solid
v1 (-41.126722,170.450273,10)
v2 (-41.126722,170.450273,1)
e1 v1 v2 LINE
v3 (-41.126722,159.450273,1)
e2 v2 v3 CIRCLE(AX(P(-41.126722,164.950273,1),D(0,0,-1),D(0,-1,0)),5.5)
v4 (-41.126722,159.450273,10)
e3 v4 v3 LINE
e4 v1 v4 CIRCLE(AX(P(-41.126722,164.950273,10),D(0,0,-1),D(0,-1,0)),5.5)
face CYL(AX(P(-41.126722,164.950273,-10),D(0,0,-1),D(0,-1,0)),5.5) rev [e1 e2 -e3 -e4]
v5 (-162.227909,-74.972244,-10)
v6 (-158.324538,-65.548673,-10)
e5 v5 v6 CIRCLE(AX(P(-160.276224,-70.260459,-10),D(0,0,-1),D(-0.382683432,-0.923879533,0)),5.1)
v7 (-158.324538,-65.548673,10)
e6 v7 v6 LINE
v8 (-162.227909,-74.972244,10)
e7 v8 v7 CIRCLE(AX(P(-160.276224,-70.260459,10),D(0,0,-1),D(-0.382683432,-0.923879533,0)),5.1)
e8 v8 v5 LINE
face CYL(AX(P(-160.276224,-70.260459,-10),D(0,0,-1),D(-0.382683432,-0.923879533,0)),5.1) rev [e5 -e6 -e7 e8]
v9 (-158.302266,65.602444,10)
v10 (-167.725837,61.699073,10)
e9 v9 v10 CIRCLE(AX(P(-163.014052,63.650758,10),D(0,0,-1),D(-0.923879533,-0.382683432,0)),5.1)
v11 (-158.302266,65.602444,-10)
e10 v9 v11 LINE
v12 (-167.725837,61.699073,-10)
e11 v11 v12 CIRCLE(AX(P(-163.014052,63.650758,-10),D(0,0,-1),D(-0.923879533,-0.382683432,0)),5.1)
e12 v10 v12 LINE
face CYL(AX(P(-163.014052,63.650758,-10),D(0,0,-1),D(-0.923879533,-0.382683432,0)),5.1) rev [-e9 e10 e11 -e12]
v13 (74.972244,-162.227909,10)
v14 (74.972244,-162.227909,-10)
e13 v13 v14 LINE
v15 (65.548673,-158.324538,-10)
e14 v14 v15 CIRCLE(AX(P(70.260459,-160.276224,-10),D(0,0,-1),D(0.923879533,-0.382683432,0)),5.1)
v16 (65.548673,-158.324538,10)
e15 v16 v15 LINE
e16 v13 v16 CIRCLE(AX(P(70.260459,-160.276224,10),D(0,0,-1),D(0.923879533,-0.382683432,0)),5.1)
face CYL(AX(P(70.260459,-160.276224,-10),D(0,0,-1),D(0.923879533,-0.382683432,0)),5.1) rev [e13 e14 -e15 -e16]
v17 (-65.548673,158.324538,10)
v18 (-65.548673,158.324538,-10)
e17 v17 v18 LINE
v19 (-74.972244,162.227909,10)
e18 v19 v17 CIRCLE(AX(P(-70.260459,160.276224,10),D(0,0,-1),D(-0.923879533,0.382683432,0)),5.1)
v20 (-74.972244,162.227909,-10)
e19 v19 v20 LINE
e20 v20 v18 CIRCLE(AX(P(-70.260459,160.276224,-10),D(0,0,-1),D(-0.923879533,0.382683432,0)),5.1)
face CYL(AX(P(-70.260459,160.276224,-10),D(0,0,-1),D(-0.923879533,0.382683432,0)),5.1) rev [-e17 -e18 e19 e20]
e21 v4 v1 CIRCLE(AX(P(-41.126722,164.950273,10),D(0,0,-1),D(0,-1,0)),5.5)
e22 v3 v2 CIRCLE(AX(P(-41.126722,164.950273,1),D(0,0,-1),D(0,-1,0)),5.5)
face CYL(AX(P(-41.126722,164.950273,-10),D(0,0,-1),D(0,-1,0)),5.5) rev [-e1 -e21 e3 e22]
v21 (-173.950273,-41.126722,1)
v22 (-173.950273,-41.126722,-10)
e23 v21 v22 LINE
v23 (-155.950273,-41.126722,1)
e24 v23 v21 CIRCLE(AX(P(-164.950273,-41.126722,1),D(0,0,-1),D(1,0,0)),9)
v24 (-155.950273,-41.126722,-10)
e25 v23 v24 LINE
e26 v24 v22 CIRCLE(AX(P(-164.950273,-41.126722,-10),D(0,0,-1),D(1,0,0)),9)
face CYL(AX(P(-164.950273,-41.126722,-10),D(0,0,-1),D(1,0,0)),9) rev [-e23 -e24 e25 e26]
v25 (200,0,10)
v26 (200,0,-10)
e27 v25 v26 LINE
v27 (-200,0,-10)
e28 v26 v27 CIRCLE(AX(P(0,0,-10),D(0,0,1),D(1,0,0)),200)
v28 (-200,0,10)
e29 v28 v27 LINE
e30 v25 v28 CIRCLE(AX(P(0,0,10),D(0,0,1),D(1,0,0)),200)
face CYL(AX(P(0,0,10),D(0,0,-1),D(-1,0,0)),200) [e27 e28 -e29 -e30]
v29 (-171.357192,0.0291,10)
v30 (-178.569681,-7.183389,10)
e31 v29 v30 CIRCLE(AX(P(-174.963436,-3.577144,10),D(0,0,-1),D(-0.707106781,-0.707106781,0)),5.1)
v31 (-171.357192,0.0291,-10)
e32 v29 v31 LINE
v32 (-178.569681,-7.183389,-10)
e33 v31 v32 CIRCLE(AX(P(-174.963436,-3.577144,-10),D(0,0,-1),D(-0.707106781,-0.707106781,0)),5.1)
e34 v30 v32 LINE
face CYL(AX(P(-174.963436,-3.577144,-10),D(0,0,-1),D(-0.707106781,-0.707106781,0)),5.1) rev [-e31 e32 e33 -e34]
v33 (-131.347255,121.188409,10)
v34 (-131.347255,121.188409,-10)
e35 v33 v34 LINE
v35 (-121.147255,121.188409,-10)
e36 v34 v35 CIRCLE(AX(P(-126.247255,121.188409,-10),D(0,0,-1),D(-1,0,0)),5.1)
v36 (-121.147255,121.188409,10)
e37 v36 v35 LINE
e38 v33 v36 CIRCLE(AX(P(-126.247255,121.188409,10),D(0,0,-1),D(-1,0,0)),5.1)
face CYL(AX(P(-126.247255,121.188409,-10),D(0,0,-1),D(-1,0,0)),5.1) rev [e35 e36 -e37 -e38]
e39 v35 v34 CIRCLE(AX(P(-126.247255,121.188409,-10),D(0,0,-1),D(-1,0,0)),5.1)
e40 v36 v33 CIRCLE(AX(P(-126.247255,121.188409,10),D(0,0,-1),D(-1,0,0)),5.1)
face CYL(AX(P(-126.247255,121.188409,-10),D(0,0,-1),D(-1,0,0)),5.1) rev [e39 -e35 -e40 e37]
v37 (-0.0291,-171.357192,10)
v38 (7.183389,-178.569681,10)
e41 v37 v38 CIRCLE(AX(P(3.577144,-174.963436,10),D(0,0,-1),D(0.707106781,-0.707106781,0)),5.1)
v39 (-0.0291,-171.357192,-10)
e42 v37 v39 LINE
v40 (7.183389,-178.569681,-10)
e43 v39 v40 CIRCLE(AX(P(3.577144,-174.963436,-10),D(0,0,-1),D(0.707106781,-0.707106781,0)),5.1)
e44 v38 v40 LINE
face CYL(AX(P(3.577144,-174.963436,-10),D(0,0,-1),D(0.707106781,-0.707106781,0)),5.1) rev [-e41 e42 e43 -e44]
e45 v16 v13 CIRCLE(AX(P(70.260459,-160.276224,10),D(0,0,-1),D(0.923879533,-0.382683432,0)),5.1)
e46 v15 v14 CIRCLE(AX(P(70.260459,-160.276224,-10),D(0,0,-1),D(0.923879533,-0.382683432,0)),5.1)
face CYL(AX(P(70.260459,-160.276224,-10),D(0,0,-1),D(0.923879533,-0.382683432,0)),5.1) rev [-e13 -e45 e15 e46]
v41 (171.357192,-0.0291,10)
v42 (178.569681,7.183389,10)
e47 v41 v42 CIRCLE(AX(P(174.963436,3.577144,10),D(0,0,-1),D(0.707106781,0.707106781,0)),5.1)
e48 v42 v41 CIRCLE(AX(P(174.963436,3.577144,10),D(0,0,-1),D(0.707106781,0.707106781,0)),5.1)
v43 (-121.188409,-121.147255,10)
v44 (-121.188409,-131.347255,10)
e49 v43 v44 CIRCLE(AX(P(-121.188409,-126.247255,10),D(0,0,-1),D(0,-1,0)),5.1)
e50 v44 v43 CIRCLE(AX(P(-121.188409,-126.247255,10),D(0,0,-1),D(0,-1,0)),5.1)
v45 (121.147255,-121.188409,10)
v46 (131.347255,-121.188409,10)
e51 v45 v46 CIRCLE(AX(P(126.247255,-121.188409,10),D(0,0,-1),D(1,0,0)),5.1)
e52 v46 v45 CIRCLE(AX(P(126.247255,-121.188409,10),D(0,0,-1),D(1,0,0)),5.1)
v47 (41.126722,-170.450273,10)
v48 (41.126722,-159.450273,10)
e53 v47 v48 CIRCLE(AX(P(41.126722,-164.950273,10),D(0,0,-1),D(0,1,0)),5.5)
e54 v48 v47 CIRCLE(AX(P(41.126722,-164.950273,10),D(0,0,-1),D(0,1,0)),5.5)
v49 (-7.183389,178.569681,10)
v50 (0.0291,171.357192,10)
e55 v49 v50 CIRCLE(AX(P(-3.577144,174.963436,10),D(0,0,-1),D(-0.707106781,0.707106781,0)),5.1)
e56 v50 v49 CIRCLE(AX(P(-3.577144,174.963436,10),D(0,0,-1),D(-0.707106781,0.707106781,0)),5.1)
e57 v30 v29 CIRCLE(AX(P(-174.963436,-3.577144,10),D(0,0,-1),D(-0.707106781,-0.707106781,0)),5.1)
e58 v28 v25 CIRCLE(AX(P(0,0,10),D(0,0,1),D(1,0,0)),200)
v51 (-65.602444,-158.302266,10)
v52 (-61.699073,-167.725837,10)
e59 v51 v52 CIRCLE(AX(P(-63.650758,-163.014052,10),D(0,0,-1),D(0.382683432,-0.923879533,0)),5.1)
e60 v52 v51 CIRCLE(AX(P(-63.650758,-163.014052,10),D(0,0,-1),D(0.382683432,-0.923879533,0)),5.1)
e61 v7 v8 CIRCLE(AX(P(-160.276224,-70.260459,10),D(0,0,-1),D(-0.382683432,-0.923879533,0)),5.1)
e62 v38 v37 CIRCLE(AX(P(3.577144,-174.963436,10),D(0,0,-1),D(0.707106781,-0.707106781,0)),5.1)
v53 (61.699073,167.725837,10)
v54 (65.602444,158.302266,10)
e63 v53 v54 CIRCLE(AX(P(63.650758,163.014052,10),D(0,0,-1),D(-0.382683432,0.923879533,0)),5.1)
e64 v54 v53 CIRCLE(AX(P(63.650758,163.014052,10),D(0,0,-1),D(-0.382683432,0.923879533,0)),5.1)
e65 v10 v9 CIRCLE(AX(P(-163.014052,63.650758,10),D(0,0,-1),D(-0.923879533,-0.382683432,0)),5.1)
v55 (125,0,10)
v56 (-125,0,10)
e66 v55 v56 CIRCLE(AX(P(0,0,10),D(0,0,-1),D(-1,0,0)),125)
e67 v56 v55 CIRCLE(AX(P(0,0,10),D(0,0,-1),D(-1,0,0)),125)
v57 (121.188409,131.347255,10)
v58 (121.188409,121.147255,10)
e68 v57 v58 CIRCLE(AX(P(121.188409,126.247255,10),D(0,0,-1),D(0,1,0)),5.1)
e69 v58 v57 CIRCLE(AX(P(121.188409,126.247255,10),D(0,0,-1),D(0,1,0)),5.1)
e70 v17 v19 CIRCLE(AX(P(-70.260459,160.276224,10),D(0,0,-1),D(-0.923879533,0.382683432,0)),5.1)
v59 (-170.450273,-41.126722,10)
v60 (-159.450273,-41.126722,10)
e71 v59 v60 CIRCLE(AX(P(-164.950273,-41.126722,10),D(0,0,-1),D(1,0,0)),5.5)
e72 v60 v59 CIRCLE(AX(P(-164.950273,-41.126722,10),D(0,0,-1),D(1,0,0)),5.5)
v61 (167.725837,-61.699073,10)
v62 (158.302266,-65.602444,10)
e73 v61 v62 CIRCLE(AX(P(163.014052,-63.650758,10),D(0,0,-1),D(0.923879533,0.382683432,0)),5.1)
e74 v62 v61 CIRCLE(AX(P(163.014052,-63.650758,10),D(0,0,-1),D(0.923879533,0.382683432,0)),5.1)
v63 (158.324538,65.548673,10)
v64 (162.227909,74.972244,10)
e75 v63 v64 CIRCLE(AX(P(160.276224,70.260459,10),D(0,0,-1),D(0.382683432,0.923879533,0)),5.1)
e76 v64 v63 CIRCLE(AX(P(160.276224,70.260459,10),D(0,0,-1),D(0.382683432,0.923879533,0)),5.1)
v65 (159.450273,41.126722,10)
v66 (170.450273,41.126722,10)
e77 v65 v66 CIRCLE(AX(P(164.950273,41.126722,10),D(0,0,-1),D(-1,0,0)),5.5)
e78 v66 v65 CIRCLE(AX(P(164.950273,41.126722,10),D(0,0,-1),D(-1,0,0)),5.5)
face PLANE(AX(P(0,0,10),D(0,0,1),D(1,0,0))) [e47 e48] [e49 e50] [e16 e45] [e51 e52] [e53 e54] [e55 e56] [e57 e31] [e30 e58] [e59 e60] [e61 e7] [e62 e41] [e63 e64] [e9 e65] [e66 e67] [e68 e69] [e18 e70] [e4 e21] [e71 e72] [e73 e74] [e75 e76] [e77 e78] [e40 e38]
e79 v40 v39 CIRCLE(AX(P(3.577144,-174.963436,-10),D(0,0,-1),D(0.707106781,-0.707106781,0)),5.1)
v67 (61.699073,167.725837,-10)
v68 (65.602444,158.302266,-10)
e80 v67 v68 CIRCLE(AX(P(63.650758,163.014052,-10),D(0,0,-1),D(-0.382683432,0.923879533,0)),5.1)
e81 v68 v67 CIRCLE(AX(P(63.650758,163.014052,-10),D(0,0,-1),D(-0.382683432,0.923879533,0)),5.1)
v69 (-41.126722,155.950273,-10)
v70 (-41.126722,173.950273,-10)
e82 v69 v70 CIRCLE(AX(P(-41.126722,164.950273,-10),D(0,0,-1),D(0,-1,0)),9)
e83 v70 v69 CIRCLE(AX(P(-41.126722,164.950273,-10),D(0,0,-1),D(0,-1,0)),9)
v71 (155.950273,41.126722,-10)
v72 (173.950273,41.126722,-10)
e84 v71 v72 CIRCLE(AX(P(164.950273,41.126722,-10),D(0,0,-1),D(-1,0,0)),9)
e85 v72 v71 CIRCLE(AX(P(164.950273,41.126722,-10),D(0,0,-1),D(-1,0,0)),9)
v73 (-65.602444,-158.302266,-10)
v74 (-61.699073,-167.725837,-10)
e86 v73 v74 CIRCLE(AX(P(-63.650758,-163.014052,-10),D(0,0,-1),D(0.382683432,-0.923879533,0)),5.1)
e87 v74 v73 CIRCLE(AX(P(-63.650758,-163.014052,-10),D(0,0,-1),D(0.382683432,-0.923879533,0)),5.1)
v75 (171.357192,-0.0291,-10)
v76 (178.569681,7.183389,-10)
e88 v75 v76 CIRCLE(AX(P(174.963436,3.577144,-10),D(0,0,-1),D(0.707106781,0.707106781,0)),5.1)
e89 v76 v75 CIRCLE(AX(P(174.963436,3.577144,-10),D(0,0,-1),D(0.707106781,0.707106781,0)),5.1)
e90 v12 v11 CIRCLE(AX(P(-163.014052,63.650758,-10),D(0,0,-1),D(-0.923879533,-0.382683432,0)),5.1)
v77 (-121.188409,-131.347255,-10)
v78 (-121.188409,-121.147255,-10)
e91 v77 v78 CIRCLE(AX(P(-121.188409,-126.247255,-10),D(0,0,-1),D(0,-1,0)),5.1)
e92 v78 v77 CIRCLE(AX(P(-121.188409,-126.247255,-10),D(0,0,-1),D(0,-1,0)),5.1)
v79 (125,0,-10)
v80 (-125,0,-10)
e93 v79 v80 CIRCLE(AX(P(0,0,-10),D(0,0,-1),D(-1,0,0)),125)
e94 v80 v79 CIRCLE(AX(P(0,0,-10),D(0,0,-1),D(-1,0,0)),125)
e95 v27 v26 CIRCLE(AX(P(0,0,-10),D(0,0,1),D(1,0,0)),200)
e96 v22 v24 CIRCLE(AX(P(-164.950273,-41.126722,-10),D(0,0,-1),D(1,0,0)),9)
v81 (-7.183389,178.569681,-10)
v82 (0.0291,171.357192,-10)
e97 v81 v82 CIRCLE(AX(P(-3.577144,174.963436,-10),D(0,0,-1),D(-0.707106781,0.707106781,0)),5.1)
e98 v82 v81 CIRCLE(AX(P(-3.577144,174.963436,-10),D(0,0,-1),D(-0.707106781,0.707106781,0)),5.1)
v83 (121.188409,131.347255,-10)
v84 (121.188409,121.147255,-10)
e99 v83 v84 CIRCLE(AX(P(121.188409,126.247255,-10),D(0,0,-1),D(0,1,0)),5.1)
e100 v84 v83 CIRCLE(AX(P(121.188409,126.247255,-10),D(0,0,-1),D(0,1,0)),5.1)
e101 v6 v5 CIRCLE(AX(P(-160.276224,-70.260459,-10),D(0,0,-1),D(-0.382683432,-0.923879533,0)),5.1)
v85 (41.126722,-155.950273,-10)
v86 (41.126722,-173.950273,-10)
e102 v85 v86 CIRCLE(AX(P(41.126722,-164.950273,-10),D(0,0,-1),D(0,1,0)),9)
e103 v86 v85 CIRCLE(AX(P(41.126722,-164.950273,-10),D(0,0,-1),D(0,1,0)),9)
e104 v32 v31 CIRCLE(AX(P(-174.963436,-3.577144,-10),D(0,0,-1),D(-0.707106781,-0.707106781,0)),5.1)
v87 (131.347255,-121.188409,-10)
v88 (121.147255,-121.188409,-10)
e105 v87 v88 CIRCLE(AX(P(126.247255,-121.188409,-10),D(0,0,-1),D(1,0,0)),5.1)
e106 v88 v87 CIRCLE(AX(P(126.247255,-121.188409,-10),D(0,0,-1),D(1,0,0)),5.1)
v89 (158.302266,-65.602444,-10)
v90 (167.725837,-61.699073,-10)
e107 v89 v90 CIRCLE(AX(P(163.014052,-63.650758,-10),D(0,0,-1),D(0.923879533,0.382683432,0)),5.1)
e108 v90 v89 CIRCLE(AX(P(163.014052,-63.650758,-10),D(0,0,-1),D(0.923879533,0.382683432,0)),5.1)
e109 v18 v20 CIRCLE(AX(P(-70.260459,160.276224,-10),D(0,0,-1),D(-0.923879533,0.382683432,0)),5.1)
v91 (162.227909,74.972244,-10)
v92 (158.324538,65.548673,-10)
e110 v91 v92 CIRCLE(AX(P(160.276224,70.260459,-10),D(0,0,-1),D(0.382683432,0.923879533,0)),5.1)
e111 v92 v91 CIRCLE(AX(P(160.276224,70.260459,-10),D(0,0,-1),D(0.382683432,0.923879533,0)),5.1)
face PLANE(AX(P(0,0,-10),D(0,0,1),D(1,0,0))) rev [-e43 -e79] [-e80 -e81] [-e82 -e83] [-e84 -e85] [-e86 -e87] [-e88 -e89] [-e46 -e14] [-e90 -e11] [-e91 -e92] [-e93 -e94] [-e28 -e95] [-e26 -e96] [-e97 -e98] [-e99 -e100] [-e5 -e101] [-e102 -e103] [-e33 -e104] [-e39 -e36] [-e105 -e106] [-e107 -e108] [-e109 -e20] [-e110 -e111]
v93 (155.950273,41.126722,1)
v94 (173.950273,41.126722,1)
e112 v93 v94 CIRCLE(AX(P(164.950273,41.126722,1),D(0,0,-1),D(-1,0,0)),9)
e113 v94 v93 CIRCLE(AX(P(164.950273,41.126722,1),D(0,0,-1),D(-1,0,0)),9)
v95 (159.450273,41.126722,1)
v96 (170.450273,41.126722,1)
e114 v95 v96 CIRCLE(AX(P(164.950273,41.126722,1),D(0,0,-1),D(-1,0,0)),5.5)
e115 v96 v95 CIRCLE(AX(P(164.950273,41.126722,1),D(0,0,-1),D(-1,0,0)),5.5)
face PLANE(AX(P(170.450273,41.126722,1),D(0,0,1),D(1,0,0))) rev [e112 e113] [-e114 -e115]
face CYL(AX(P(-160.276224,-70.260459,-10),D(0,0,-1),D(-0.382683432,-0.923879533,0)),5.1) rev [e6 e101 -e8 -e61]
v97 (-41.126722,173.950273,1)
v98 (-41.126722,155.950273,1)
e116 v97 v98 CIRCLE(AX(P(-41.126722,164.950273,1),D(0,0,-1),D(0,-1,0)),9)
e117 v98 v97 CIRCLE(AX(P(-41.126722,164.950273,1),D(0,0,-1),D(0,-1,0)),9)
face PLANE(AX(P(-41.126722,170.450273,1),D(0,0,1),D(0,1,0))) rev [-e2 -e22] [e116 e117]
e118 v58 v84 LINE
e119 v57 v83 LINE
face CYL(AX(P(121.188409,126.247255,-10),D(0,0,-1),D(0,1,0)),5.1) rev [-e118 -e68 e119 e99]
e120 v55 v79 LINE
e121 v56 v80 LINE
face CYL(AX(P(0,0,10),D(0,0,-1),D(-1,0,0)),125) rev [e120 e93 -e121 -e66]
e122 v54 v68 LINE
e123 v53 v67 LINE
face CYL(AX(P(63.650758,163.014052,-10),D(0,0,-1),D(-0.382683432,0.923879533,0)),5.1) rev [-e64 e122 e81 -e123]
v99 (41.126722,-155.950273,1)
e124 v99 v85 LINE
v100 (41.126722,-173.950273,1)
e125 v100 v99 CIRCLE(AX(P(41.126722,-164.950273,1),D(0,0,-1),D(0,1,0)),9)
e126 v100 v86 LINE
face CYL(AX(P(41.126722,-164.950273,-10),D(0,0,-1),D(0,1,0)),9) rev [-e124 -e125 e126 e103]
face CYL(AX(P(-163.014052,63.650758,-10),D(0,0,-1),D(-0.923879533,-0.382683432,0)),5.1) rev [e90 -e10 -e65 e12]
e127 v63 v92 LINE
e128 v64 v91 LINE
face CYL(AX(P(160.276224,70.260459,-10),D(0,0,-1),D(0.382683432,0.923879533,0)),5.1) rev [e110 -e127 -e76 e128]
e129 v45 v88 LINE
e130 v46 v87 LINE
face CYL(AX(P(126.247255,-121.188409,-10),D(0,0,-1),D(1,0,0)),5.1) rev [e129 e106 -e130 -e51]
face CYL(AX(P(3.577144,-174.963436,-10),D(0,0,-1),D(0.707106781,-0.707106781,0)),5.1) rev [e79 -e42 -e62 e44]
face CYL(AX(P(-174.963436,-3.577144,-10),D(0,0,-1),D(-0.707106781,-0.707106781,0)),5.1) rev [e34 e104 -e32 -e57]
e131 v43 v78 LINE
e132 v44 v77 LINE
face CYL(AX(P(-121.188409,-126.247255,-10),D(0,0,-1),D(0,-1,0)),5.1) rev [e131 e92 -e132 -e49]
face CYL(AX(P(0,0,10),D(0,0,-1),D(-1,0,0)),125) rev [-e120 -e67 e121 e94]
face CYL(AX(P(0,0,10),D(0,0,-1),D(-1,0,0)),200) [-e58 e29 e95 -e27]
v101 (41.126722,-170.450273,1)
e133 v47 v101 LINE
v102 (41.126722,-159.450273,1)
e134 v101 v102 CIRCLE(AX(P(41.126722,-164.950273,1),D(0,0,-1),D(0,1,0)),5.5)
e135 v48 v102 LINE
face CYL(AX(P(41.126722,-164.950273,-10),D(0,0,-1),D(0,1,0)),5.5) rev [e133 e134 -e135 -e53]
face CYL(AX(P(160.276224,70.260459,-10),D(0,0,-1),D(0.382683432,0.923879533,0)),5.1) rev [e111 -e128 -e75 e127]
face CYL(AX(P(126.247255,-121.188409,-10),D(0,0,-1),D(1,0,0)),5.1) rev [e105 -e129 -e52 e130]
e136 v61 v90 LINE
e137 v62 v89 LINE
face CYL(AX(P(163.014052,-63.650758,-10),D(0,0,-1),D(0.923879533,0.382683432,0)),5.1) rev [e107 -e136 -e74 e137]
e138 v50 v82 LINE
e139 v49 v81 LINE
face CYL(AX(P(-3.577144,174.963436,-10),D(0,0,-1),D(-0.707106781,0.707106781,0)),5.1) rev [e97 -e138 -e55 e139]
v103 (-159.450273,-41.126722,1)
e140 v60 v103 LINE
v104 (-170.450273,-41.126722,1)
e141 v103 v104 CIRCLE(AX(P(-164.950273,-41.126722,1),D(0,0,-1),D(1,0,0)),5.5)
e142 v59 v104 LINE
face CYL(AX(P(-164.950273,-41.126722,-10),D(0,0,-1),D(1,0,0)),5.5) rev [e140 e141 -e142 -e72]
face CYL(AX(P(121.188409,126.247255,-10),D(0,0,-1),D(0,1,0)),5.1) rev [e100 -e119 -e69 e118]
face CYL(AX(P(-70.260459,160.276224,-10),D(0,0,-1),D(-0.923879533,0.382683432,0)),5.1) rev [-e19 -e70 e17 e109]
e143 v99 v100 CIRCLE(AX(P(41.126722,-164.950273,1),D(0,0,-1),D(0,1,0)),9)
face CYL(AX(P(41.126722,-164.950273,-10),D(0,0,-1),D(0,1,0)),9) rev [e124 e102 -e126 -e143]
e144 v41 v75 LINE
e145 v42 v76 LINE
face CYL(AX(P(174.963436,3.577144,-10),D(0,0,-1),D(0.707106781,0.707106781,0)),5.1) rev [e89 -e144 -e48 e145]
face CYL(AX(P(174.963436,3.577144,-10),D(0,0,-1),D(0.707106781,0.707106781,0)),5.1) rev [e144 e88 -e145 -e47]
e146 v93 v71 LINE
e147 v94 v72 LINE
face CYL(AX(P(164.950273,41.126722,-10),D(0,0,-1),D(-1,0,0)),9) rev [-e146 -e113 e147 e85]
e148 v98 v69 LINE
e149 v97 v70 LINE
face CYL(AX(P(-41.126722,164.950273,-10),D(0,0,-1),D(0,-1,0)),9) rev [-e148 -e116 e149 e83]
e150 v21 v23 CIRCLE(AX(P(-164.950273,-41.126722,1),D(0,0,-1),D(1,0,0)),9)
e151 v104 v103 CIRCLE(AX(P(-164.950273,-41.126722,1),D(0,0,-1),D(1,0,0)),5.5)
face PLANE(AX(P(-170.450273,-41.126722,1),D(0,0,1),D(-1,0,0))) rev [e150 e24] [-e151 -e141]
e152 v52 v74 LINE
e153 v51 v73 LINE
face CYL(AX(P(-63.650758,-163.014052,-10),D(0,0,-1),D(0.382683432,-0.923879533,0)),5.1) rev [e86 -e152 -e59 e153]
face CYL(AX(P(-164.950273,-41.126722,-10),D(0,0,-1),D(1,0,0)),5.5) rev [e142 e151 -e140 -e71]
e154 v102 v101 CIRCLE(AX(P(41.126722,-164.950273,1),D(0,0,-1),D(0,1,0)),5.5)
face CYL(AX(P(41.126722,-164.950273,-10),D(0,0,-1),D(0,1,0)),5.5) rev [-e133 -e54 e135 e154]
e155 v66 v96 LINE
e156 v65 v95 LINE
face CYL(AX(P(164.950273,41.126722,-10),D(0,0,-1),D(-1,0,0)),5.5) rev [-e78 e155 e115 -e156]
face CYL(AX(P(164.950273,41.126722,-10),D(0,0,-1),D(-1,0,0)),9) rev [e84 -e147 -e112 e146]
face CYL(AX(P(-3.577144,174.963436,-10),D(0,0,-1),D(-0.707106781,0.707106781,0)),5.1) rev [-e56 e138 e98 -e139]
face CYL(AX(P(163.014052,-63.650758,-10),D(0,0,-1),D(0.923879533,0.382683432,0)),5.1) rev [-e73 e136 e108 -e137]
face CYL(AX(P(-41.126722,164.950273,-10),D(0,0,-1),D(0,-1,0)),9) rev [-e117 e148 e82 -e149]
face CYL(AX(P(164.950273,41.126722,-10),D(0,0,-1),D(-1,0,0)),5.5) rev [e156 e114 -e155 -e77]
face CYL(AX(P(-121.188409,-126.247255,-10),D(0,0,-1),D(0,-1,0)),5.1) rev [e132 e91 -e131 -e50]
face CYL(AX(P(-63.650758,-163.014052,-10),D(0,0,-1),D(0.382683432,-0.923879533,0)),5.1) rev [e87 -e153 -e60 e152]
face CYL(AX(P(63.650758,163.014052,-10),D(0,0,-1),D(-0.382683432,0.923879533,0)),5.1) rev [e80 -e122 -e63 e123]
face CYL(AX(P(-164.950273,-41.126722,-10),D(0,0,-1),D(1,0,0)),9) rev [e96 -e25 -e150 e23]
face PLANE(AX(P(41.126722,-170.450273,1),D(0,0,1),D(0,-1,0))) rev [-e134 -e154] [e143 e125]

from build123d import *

# Parameters (mm, degrees)
SKETCH_1_R                = 200
EXTRUDE_1_DEPTH           = 10
SKETCH_2_R                = 125
CUT_EXTRUDE_1_DEPTH       = 284.548937575
HOLE_WIZARD_M12_1_D       = 10.2
PATTERN_CIRCULAR_1_COUNT  = 16
HOLE_WIZARD_1_D           = 11
HOLE_WIZARD_1_CBORE_D     = 18
HOLE_WIZARD_1_CBORE_DEPTH = 11
PATTERN_CIRCULAR_2_COUNT  = 4


with BuildPart() as part:
    # 草图1 → 凸台-拉伸1 (new, symmetric)
    with BuildSketch(Plane.XY):
        Circle(SKETCH_1_R)
    extrude(amount=EXTRUDE_1_DEPTH, both=True)

    # 草图2 → 切除-拉伸1 (cut, through all)
    with BuildSketch(Plane(origin=(0, 0, -10), x_dir=(-1, 0, 0), z_dir=(0, 0, -1))):
        Circle(SKETCH_2_R)
    extrude(amount=-CUT_EXTRUDE_1_DEPTH, mode=Mode.SUBTRACT)

    # M12 螺纹孔1 (through all)
    with Locations(Plane(origin=(0, 0, -10), x_dir=(-1, 0, 0), z_dir=(0, 0, -1))):
        with Locations((126.247255109, 121.188409419)):
            hole_wizard_m12_1 = Hole(HOLE_WIZARD_M12_1_D / 2)

    # 阵列(圆周)1: M12 螺纹孔1 ×16 about axis
    pattern_circular_1_axis = Axis((0, 0, 0), (0, 0, 1))
    for i in range(1, PATTERN_CIRCULAR_1_COUNT):
        add(hole_wizard_m12_1.rotate(pattern_circular_1_axis, i * 360 / PATTERN_CIRCULAR_1_COUNT), mode=Mode.SUBTRACT)

    # 打孔尺寸(%根据)内六角圆柱头螺钉的类型1 (through all)
    with Locations(Plane(origin=(0, 0, -10), x_dir=(-1, 0, 0), z_dir=(0, 0, -1))):
        with Locations((-164.950273467, 41.126722252)):
            hole_wizard_1 = CounterBoreHole(HOLE_WIZARD_1_D / 2, HOLE_WIZARD_1_CBORE_D / 2, HOLE_WIZARD_1_CBORE_DEPTH)

    # 阵列(圆周)2: 打孔尺寸(%根据)内六角圆柱头螺钉的类型1 ×4 about axis
    pattern_circular_2_axis = Axis((0, 0, 0), (0, 0, 1))
    for i in range(1, PATTERN_CIRCULAR_2_COUNT):
        add(hole_wizard_1.rotate(pattern_circular_2_axis, i * 360 / PATTERN_CIRCULAR_2_COUNT), mode=Mode.SUBTRACT)


solid = part.part
